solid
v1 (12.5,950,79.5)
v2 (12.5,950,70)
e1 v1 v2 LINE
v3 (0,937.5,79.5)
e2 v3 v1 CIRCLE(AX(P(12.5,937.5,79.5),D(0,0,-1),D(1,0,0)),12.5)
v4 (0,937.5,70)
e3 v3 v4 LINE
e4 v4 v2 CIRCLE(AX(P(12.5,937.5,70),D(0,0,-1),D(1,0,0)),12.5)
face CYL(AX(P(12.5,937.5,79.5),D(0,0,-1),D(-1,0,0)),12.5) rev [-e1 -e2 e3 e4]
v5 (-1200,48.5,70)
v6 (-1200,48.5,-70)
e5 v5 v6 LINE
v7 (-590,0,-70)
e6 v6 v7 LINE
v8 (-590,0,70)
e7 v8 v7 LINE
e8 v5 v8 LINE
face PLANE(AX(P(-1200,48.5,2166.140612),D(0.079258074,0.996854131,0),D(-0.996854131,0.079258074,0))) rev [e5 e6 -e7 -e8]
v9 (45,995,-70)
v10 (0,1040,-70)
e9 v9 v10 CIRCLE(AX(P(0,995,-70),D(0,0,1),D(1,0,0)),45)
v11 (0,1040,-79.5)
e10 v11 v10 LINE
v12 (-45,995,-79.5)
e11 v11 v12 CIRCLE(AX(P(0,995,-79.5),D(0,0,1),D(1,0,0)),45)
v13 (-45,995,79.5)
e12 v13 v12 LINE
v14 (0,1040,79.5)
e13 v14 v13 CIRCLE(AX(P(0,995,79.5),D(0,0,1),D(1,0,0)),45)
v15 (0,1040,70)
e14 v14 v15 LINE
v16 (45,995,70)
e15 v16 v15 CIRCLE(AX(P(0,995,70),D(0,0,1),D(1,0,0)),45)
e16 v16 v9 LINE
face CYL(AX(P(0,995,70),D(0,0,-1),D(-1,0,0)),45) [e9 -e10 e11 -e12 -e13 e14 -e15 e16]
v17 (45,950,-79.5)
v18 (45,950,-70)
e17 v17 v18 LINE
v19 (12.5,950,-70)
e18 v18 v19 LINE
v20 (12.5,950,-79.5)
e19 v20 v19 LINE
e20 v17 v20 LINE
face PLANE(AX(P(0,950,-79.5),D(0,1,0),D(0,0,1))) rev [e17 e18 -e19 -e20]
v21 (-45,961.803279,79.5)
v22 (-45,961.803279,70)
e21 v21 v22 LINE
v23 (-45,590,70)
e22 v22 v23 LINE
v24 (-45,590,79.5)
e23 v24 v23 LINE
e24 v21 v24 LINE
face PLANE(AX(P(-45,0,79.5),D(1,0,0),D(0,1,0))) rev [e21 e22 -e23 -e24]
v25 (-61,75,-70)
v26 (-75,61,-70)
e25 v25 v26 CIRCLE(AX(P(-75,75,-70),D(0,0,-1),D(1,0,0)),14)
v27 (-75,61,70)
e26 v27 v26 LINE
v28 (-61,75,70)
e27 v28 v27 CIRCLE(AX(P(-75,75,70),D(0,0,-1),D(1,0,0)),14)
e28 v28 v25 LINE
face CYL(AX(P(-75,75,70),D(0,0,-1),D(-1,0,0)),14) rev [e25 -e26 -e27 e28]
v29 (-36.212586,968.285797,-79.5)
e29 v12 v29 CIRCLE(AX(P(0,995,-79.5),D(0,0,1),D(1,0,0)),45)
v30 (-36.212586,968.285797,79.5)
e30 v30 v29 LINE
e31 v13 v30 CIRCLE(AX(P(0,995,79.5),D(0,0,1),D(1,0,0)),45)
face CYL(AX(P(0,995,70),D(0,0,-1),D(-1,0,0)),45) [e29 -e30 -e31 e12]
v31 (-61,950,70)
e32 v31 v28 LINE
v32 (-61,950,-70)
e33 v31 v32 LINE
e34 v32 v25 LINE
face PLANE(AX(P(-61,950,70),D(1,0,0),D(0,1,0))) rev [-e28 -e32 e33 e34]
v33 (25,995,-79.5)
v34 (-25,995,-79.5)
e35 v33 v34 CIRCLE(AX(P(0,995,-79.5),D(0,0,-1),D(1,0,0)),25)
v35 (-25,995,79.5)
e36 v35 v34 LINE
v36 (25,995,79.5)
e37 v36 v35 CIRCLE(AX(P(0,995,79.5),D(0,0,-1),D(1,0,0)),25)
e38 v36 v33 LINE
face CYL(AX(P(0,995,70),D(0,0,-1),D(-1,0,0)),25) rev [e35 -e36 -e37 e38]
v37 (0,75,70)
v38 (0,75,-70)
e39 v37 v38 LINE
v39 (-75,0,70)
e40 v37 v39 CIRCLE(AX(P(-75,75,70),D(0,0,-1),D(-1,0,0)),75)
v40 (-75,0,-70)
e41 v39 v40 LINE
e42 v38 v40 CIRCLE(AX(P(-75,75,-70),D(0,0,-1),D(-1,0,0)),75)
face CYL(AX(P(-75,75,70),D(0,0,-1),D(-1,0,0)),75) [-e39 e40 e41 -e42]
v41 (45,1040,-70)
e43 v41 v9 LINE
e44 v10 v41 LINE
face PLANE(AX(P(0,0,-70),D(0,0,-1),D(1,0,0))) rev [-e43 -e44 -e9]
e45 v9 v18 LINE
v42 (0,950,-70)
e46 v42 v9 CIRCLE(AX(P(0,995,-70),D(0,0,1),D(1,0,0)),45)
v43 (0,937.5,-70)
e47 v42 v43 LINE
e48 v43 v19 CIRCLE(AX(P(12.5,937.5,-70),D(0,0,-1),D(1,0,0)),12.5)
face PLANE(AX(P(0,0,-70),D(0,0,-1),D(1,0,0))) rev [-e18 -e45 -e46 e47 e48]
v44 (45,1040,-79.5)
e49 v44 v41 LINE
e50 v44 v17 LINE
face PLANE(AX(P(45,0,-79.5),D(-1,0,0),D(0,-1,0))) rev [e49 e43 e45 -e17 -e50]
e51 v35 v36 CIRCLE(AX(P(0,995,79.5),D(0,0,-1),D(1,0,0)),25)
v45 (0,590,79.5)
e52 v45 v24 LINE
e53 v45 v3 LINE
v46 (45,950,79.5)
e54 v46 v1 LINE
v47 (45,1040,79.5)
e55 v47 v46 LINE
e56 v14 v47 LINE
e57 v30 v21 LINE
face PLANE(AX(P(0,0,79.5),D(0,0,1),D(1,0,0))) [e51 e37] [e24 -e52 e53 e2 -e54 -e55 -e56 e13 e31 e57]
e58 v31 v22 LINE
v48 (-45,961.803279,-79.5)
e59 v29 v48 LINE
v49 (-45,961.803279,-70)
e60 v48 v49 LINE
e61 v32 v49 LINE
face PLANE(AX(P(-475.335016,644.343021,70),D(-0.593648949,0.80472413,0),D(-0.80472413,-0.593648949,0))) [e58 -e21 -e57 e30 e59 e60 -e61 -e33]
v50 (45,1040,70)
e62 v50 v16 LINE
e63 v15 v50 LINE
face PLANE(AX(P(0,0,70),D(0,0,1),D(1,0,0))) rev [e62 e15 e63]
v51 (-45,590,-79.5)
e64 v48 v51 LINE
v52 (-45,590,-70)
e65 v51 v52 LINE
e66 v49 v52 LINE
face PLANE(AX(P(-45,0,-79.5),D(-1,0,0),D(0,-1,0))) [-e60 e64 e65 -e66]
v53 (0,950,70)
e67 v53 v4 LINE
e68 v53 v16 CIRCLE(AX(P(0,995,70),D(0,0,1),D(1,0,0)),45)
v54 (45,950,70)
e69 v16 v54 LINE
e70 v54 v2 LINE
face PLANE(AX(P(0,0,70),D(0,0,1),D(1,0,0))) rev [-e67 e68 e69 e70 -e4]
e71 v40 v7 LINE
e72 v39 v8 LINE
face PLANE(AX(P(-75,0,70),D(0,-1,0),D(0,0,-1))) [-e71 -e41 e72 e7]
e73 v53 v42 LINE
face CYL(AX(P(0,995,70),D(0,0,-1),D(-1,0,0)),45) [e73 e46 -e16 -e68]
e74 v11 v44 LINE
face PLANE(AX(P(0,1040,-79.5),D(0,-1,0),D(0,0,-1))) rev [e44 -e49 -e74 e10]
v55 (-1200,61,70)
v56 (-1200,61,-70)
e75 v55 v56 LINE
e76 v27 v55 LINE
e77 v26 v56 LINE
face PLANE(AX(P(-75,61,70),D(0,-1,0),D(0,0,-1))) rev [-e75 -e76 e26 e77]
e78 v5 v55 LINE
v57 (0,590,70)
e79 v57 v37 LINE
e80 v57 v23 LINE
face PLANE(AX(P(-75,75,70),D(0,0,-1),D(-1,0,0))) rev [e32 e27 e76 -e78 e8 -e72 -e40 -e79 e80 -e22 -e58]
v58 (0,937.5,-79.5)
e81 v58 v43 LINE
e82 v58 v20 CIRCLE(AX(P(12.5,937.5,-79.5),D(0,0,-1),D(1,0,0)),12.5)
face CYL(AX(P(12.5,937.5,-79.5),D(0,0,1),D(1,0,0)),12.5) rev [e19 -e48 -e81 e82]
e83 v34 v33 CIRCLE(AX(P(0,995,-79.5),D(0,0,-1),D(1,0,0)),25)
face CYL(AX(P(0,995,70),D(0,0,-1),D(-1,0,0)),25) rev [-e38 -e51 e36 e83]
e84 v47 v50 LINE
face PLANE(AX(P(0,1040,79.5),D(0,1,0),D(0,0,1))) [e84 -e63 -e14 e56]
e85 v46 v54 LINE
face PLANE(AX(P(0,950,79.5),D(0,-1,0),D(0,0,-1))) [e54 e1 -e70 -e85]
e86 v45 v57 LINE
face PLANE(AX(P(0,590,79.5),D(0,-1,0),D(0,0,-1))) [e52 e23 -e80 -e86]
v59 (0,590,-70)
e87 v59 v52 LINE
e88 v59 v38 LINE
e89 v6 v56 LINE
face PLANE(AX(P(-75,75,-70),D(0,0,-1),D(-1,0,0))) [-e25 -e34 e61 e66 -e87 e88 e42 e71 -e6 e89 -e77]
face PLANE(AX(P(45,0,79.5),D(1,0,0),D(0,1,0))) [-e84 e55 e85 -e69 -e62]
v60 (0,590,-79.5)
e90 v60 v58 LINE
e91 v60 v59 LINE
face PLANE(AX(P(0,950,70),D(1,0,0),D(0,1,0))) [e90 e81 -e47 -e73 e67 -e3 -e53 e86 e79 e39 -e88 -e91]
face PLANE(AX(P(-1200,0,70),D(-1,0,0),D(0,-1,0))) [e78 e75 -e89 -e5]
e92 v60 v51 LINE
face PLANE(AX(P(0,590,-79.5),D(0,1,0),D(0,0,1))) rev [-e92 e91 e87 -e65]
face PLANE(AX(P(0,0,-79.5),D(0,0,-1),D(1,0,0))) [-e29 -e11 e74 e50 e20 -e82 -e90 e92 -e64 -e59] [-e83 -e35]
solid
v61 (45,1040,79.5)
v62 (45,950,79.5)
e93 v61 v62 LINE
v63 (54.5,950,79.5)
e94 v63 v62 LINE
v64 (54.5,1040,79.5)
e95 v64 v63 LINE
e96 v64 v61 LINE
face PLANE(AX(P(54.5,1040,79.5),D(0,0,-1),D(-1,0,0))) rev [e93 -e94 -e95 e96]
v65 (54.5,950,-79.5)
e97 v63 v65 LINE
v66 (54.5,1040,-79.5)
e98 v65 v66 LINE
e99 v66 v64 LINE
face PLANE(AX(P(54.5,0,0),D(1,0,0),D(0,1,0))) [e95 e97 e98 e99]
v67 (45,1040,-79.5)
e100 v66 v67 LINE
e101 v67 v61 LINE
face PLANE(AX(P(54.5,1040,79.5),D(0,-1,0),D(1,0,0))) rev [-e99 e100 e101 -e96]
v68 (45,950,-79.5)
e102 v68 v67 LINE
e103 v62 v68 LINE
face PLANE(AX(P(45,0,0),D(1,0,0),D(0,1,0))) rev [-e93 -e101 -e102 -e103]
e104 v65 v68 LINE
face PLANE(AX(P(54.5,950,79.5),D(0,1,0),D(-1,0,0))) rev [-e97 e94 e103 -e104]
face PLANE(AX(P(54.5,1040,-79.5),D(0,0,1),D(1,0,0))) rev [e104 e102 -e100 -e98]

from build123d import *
from build123d.topology import SkipClean

# Parameters (mm, degrees)
FORK_BLADE_AND_SHANK_DEPTH     = 70
BLADE_TIP_TAPER_CUT_DEPTH      = 1537.912489376
BLADE_TIP_TAPER_CUT_DEPTH_BACK = 1537.912489376
SHANK_BOSS_SKETCH_R            = 45
SHANK_BOSS_SKETCH_R_2          = 25
SHANK_LOWER_BOSS_DEPTH         = 70
SHANK_UPPER_BOSS_DEPTH         = 70
SIDE_START                     = 9.5
SIDE_PLATE_SKETCH_R            = 25
SIDE_PLATE_DEPTH               = 9.5
TOP_HOOK_BLOCK_SKETCH_W        = 159
TOP_HOOK_BLOCK_SKETCH_H        = 90
TOP_HOOK_BLOCK_DEPTH           = 9.5


with BuildPart() as part:
    # Fork L-Profile Sketch → Fork Blade and Shank (new, symmetric)
    with BuildSketch(Plane.XY):
        with BuildLine():
            Line((0, 950), (0, 75))
            ThreePointArc((0, 75), (-21.966991411, 21.966991411), (-75, 0))
            Line((-75, 0), (-1200, 0))
            Line((-1200, 0), (-1200, 61))
            Line((-1200, 61), (-75, 61))
            ThreePointArc((-75, 61), (-65.100505063, 65.100505063), (-61, 75))
            Line((-61, 75), (-61, 950))
            Line((-61, 950), (0, 950))
        make_face()
    extrude(amount=FORK_BLADE_AND_SHANK_DEPTH, both=True)

    # Blade Taper Sketch → Blade Tip Taper Cut (cut, two sides: drawn at the far end of the back side and taken through both)
    with BuildSketch(Plane.XY.offset(70).offset(-BLADE_TIP_TAPER_CUT_DEPTH_BACK)):
        Polygon((-4202.326226889, 287.209544269), (-1200, 48.5), (-590, 0), (2412.326226889, -238.709544269), (1934.907138351, -6243.361998046), (-4679.745315427, -5717.442909508), align=None)
    extrude(amount=BLADE_TIP_TAPER_CUT_DEPTH + BLADE_TIP_TAPER_CUT_DEPTH_BACK, mode=Mode.SUBTRACT)



with BuildPart() as body_2:
    # Shank Boss Sketch → Shank Lower Boss (new, symmetric)
    with BuildSketch(Plane.XY):
        with Locations((0, 995)):
            Circle(SHANK_BOSS_SKETCH_R)
        with Locations((0, 995)):
            Circle(SHANK_BOSS_SKETCH_R_2, mode=Mode.SUBTRACT)
    extrude(amount=SHANK_LOWER_BOSS_DEPTH, both=True)


with BuildPart() as part_1:
    add(part.part)

    add(body_2.part)  # Shank Upper Boss merges body 2
    # Shank Upper Boss Sketch → Shank Upper Boss (add, symmetric)
    with BuildSketch(Plane.XY):
        with BuildLine():
            Line((-36.212585863, 968.285797314), (-61, 950))
            Line((-61, 950), (0, 950))
            ThreePointArc((0, 950), (-20.283748164, 954.830738612), (-36.212585863, 968.285797314))
        make_face()
    extrude(amount=SHANK_UPPER_BOSS_DEPTH, both=True)

    # Side Plate Sketch → Side Plate (add)
    # profile 1 of 4: a face of its own
    with BuildSketch(Plane.XY.offset(70).offset(SIDE_START)):
        with BuildLine():
            Line((45, 1040), (0, 1040))
            ThreePointArc((0, 1040), (31.819805153, 1026.819805153), (45, 995))
            Line((45, 995), (45, 1040))
        make_face()
    # profile 2 of 4: a face of its own
    with BuildSketch(Plane.XY.offset(70).offset(SIDE_START)):
        with BuildLine():
            Line((45, 950), (45, 995))
            ThreePointArc((45, 995), (31.819805153, 963.180194847), (0, 950))
            Line((0, 950), (0, 937.5))
            ThreePointArc((0, 937.5), (3.661165235, 946.338834765), (12.5, 950))
            Line((12.5, 950), (45, 950))
        make_face()
    # profile 3 of 4: a face of its own
    with BuildSketch(Plane.XY.offset(70).offset(SIDE_START)):
        with BuildLine():
            ThreePointArc((0, 1040), (-31.819805153, 1026.819805153), (-45, 995))
            ThreePointArc((-45, 995), (-42.746732997, 980.938818752), (-36.212585863, 968.285797314))
            Line((-36.212585863, 968.285797314), (-45, 961.803278689))
            Line((-45, 961.803278689), (-45, 950))
            Line((-45, 950), (0, 950))
            ThreePointArc((0, 950), (31.819805153, 963.180194847), (45, 995))
            ThreePointArc((45, 995), (31.819805153, 1026.819805153), (0, 1040))
        make_face()
        with Locations((0, 995)):
            Circle(SIDE_PLATE_SKETCH_R, mode=Mode.SUBTRACT)
    # profile 4 of 4: a face of its own
    with BuildSketch(Plane.XY.offset(70).offset(SIDE_START)):
        Polygon((0, 950), (-45, 950), (-45, 590), (0, 590), (0, 937.5), align=None)
    side_plate = extrude(amount=-SIDE_PLATE_DEPTH)

    # Side Plate Mirror: Side Plate across plane
    with SkipClean():  # the faces are left unmerged after this step: merging them gives an invalid solid
        add(side_plate.mirror(Plane.XY))


with BuildPart() as body_2_2:
    # Top Hook Block Sketch → Top Hook Block (new body)
    with BuildSketch(Plane(origin=(45, 0, 0), x_dir=(0, 0, -1), z_dir=(1, 0, 0))):
        with Locations((0, 995)):
            Rectangle(TOP_HOOK_BLOCK_SKETCH_W, TOP_HOOK_BLOCK_SKETCH_H)
    extrude(amount=TOP_HOOK_BLOCK_DEPTH)


solid = Compound([part_1.part, body_2_2.part])
